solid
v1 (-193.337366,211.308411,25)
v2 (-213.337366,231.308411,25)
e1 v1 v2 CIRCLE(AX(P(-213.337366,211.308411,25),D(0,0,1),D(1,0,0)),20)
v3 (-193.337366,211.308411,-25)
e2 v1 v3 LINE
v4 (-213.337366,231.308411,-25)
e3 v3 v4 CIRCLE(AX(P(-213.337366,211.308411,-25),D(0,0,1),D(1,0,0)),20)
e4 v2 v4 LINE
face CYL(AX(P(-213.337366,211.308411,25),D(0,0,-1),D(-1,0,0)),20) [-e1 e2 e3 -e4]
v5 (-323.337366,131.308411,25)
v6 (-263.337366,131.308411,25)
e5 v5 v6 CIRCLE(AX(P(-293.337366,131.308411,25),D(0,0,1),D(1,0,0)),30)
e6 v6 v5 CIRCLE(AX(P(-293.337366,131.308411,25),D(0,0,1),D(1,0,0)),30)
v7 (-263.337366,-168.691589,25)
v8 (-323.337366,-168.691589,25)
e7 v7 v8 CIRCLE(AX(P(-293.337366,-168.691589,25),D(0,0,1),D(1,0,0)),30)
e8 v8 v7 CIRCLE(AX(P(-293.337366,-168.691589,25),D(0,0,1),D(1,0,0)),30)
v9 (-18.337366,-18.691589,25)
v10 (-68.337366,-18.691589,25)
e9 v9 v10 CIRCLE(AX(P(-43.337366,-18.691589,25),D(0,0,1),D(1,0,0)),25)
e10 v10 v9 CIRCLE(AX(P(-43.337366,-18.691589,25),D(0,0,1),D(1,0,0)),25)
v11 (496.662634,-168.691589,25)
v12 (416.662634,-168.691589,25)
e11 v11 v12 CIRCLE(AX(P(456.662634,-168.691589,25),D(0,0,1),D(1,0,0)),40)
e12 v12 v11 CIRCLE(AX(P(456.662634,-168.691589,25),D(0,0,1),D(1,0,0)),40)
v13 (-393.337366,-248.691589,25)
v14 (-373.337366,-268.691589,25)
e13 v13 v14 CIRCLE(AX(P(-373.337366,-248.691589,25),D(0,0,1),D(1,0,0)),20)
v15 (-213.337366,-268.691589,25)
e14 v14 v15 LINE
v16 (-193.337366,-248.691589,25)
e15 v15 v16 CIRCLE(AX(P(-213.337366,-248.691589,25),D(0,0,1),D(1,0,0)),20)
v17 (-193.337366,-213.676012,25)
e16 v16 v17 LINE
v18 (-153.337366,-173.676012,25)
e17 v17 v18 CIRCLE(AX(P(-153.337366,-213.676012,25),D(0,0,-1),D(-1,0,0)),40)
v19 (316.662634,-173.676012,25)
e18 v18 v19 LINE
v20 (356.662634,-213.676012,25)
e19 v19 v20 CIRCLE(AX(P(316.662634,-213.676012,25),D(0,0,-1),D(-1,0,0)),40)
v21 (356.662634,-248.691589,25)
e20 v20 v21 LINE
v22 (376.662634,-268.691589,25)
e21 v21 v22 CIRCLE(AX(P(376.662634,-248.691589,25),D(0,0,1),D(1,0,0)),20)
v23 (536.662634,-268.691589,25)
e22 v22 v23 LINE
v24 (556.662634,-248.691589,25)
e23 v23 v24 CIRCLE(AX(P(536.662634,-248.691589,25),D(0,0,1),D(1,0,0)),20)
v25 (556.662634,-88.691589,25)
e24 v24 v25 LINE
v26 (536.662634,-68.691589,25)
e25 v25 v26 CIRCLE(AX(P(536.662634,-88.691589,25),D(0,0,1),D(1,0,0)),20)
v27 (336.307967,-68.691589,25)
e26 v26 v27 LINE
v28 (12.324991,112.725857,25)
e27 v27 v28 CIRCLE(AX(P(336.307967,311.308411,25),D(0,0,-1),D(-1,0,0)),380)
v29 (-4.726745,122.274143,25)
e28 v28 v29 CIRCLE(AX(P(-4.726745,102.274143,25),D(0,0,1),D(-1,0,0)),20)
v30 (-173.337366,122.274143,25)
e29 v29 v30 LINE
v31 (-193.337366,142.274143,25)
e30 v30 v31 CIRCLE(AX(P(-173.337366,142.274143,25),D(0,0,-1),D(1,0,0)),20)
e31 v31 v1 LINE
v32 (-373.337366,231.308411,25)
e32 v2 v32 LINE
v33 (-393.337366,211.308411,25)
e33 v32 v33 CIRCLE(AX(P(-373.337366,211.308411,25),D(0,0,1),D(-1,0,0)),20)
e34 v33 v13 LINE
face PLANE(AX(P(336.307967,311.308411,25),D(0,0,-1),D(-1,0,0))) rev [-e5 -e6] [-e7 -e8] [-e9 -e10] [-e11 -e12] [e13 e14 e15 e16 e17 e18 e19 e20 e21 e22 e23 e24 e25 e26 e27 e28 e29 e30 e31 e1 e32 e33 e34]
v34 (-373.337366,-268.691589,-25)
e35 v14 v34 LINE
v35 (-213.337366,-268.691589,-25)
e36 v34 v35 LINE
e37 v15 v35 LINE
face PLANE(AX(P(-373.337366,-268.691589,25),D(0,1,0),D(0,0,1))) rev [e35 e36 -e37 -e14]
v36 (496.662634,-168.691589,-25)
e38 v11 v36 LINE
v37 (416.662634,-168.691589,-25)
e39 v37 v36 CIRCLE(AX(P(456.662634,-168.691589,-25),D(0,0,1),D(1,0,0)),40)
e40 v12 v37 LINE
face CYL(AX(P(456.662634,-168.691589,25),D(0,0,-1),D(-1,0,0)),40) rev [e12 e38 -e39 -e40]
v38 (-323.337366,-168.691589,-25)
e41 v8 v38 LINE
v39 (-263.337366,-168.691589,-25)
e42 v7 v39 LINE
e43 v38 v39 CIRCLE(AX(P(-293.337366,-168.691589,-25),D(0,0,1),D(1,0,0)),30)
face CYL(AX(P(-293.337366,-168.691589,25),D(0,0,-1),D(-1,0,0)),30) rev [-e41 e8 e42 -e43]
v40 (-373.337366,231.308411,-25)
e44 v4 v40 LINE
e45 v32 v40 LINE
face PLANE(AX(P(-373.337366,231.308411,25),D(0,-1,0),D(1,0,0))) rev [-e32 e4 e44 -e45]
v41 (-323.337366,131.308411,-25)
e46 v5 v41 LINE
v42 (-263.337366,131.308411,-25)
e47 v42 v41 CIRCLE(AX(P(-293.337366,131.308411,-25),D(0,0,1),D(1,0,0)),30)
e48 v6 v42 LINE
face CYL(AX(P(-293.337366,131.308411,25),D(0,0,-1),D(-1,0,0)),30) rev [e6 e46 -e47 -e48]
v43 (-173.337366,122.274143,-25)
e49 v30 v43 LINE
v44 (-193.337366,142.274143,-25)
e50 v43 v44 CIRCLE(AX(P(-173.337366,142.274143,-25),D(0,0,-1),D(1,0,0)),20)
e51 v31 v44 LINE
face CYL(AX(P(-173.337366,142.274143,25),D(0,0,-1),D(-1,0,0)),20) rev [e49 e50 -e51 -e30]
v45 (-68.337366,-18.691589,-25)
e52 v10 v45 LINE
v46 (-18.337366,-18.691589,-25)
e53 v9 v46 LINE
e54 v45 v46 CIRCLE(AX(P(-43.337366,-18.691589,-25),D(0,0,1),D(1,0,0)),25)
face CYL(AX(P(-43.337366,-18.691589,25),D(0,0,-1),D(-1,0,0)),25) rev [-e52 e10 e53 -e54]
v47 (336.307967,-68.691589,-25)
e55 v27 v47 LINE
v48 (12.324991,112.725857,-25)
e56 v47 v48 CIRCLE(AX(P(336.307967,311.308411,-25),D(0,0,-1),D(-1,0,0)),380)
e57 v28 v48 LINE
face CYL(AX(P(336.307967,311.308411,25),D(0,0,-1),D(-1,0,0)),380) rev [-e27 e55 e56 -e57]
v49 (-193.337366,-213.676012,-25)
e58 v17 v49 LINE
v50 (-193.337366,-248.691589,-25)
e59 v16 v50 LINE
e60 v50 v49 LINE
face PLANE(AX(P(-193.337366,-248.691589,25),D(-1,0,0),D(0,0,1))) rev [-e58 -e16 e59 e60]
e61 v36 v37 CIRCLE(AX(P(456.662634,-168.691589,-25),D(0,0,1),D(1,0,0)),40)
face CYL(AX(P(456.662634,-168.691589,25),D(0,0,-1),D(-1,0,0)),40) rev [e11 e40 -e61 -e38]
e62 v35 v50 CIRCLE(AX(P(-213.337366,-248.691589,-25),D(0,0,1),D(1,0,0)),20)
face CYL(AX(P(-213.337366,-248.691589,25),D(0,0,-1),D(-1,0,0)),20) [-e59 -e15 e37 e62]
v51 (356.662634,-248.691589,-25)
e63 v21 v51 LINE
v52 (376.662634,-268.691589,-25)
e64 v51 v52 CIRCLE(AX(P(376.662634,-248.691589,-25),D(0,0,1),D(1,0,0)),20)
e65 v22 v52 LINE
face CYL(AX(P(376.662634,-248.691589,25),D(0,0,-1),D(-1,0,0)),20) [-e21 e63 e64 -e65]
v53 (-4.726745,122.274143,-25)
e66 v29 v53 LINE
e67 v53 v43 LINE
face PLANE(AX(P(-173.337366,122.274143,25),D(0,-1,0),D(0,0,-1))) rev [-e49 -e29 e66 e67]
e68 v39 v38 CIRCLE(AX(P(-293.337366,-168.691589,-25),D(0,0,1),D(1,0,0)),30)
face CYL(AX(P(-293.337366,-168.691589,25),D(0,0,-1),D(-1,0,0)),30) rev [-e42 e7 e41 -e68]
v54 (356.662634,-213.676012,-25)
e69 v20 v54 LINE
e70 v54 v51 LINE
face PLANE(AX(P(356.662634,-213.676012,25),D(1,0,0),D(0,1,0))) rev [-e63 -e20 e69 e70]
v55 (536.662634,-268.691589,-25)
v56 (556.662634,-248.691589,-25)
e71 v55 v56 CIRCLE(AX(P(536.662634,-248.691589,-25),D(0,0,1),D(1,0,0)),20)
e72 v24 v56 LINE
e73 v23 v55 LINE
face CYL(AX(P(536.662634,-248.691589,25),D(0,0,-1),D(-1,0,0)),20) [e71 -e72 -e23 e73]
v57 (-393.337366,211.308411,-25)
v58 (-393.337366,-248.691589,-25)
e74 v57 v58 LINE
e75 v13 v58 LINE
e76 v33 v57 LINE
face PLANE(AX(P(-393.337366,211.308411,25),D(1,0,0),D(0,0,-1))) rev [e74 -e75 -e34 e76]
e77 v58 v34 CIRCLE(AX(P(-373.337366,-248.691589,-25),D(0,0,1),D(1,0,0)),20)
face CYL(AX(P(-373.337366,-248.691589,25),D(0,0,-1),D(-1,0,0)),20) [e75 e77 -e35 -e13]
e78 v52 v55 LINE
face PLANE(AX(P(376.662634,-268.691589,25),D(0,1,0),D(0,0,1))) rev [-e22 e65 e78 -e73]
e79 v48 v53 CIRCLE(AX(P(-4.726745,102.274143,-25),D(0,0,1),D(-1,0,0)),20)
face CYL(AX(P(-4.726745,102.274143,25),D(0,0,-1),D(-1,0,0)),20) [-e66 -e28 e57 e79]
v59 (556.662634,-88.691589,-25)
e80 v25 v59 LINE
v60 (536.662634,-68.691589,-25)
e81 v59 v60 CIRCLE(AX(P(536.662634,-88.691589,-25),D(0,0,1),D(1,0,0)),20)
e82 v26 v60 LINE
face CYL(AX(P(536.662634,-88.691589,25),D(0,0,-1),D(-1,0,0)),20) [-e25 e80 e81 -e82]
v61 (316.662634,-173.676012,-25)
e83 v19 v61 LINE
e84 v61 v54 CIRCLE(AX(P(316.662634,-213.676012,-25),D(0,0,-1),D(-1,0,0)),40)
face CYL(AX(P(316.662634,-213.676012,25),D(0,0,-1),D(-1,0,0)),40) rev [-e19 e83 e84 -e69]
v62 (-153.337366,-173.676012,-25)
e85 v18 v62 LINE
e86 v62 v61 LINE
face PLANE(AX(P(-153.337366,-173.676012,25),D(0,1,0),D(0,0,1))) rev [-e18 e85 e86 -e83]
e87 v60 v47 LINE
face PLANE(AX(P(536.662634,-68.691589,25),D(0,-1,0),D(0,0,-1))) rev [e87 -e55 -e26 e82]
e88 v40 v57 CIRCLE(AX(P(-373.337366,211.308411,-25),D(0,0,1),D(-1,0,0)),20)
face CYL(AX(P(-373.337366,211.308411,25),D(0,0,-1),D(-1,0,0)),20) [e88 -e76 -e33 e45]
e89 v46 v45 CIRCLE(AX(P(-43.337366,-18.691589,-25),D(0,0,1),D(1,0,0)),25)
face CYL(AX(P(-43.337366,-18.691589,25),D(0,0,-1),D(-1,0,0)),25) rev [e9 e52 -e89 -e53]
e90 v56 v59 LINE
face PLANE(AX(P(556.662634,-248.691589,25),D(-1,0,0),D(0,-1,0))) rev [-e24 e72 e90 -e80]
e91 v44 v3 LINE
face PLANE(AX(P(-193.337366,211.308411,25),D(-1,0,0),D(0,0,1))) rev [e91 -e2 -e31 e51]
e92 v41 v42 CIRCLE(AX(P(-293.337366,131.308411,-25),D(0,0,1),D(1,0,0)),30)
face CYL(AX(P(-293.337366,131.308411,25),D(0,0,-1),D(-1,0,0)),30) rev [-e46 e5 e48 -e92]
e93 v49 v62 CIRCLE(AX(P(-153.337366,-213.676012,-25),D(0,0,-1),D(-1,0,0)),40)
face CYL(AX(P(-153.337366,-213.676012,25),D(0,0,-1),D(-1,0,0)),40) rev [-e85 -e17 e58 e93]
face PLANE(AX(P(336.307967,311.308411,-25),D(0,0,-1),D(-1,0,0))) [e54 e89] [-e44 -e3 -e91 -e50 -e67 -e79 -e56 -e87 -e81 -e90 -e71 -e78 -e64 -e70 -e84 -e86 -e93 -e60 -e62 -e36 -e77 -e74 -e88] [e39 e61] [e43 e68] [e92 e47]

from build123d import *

# Parameters (mm, degrees)
BRACKET_PROFILE_SKETCH_R   = 30
BRACKET_PROFILE_SKETCH_R_2 = 25
BRACKET_PROFILE_SKETCH_R_3 = 40
BRACKET_PLATE_50MM_DEPTH   = 25


with BuildPart() as part:
    # Bracket Profile Sketch → Bracket Plate 50mm (new, symmetric)
    with BuildSketch(Plane.XY):
        with BuildLine():
            Line((-393.337365548, 211.308411215), (-393.337365548, -248.691588785))
            ThreePointArc((-393.337365548, -248.691588785), (-387.479501171, -262.833724409), (-373.337365548, -268.691588785))
            Line((-373.337365548, -268.691588785), (-213.337365548, -268.691588785))
            ThreePointArc((-213.337365548, -268.691588785), (-199.195229924, -262.833724409), (-193.337365548, -248.691588785))
            Line((-193.337365548, -248.691588785), (-193.337365548, -213.676012461))
            ThreePointArc((-193.337365548, -213.676012461), (-181.621636795, -185.391741214), (-153.337365548, -173.676012461))
            Line((-153.337365548, -173.676012461), (316.662634452, -173.676012461))
            ThreePointArc((316.662634452, -173.676012461), (344.9469057, -185.391741214), (356.662634452, -213.676012461))
            Line((356.662634452, -213.676012461), (356.662634452, -248.691588785))
            ThreePointArc((356.662634452, -248.691588785), (362.520498829, -262.833724409), (376.662634452, -268.691588785))
            Line((376.662634452, -268.691588785), (536.662634452, -268.691588785))
            ThreePointArc((536.662634452, -268.691588785), (550.804770076, -262.833724409), (556.662634452, -248.691588785))
            Line((556.662634452, -248.691588785), (556.662634452, -88.691588785))
            ThreePointArc((556.662634452, -88.691588785), (550.804770076, -74.549453161), (536.662634452, -68.691588785))
            Line((536.662634452, -68.691588785), (336.307967431, -68.691588785))
            ThreePointArc((336.307967431, -68.691588785), (150.648831804, -20.2495556), (12.324990963, 112.725856698))
            ThreePointArc((12.324990963, 112.725856698), (5.044788813, 119.724562608), (-4.726744641, 122.274143302))
            Line((-4.726744641, 122.274143302), (-173.337365548, 122.274143302))
            ThreePointArc((-173.337365548, 122.274143302), (-187.479501171, 128.132007678), (-193.337365548, 142.274143302))
            Line((-193.337365548, 142.274143302), (-193.337365548, 211.308411215))
            ThreePointArc((-193.337365548, 211.308411215), (-199.195229924, 225.450546839), (-213.337365548, 231.308411215))
            Line((-213.337365548, 231.308411215), (-373.337365548, 231.308411215))
            ThreePointArc((-373.337365548, 231.308411215), (-387.479501171, 225.450546839), (-393.337365548, 211.308411215))
        make_face()
        with Locations((-293.337365548, 131.308411215)):
            Circle(BRACKET_PROFILE_SKETCH_R, mode=Mode.SUBTRACT)
        with Locations((-293.337365548, -168.691588785)):
            Circle(BRACKET_PROFILE_SKETCH_R, mode=Mode.SUBTRACT)
        with Locations((-43.337365548, -18.691588785)):
            Circle(BRACKET_PROFILE_SKETCH_R_2, mode=Mode.SUBTRACT)
        with Locations((456.662634452, -168.691588785)):
            Circle(BRACKET_PROFILE_SKETCH_R_3, mode=Mode.SUBTRACT)
    extrude(amount=BRACKET_PLATE_50MM_DEPTH, both=True)


solid = part.part
